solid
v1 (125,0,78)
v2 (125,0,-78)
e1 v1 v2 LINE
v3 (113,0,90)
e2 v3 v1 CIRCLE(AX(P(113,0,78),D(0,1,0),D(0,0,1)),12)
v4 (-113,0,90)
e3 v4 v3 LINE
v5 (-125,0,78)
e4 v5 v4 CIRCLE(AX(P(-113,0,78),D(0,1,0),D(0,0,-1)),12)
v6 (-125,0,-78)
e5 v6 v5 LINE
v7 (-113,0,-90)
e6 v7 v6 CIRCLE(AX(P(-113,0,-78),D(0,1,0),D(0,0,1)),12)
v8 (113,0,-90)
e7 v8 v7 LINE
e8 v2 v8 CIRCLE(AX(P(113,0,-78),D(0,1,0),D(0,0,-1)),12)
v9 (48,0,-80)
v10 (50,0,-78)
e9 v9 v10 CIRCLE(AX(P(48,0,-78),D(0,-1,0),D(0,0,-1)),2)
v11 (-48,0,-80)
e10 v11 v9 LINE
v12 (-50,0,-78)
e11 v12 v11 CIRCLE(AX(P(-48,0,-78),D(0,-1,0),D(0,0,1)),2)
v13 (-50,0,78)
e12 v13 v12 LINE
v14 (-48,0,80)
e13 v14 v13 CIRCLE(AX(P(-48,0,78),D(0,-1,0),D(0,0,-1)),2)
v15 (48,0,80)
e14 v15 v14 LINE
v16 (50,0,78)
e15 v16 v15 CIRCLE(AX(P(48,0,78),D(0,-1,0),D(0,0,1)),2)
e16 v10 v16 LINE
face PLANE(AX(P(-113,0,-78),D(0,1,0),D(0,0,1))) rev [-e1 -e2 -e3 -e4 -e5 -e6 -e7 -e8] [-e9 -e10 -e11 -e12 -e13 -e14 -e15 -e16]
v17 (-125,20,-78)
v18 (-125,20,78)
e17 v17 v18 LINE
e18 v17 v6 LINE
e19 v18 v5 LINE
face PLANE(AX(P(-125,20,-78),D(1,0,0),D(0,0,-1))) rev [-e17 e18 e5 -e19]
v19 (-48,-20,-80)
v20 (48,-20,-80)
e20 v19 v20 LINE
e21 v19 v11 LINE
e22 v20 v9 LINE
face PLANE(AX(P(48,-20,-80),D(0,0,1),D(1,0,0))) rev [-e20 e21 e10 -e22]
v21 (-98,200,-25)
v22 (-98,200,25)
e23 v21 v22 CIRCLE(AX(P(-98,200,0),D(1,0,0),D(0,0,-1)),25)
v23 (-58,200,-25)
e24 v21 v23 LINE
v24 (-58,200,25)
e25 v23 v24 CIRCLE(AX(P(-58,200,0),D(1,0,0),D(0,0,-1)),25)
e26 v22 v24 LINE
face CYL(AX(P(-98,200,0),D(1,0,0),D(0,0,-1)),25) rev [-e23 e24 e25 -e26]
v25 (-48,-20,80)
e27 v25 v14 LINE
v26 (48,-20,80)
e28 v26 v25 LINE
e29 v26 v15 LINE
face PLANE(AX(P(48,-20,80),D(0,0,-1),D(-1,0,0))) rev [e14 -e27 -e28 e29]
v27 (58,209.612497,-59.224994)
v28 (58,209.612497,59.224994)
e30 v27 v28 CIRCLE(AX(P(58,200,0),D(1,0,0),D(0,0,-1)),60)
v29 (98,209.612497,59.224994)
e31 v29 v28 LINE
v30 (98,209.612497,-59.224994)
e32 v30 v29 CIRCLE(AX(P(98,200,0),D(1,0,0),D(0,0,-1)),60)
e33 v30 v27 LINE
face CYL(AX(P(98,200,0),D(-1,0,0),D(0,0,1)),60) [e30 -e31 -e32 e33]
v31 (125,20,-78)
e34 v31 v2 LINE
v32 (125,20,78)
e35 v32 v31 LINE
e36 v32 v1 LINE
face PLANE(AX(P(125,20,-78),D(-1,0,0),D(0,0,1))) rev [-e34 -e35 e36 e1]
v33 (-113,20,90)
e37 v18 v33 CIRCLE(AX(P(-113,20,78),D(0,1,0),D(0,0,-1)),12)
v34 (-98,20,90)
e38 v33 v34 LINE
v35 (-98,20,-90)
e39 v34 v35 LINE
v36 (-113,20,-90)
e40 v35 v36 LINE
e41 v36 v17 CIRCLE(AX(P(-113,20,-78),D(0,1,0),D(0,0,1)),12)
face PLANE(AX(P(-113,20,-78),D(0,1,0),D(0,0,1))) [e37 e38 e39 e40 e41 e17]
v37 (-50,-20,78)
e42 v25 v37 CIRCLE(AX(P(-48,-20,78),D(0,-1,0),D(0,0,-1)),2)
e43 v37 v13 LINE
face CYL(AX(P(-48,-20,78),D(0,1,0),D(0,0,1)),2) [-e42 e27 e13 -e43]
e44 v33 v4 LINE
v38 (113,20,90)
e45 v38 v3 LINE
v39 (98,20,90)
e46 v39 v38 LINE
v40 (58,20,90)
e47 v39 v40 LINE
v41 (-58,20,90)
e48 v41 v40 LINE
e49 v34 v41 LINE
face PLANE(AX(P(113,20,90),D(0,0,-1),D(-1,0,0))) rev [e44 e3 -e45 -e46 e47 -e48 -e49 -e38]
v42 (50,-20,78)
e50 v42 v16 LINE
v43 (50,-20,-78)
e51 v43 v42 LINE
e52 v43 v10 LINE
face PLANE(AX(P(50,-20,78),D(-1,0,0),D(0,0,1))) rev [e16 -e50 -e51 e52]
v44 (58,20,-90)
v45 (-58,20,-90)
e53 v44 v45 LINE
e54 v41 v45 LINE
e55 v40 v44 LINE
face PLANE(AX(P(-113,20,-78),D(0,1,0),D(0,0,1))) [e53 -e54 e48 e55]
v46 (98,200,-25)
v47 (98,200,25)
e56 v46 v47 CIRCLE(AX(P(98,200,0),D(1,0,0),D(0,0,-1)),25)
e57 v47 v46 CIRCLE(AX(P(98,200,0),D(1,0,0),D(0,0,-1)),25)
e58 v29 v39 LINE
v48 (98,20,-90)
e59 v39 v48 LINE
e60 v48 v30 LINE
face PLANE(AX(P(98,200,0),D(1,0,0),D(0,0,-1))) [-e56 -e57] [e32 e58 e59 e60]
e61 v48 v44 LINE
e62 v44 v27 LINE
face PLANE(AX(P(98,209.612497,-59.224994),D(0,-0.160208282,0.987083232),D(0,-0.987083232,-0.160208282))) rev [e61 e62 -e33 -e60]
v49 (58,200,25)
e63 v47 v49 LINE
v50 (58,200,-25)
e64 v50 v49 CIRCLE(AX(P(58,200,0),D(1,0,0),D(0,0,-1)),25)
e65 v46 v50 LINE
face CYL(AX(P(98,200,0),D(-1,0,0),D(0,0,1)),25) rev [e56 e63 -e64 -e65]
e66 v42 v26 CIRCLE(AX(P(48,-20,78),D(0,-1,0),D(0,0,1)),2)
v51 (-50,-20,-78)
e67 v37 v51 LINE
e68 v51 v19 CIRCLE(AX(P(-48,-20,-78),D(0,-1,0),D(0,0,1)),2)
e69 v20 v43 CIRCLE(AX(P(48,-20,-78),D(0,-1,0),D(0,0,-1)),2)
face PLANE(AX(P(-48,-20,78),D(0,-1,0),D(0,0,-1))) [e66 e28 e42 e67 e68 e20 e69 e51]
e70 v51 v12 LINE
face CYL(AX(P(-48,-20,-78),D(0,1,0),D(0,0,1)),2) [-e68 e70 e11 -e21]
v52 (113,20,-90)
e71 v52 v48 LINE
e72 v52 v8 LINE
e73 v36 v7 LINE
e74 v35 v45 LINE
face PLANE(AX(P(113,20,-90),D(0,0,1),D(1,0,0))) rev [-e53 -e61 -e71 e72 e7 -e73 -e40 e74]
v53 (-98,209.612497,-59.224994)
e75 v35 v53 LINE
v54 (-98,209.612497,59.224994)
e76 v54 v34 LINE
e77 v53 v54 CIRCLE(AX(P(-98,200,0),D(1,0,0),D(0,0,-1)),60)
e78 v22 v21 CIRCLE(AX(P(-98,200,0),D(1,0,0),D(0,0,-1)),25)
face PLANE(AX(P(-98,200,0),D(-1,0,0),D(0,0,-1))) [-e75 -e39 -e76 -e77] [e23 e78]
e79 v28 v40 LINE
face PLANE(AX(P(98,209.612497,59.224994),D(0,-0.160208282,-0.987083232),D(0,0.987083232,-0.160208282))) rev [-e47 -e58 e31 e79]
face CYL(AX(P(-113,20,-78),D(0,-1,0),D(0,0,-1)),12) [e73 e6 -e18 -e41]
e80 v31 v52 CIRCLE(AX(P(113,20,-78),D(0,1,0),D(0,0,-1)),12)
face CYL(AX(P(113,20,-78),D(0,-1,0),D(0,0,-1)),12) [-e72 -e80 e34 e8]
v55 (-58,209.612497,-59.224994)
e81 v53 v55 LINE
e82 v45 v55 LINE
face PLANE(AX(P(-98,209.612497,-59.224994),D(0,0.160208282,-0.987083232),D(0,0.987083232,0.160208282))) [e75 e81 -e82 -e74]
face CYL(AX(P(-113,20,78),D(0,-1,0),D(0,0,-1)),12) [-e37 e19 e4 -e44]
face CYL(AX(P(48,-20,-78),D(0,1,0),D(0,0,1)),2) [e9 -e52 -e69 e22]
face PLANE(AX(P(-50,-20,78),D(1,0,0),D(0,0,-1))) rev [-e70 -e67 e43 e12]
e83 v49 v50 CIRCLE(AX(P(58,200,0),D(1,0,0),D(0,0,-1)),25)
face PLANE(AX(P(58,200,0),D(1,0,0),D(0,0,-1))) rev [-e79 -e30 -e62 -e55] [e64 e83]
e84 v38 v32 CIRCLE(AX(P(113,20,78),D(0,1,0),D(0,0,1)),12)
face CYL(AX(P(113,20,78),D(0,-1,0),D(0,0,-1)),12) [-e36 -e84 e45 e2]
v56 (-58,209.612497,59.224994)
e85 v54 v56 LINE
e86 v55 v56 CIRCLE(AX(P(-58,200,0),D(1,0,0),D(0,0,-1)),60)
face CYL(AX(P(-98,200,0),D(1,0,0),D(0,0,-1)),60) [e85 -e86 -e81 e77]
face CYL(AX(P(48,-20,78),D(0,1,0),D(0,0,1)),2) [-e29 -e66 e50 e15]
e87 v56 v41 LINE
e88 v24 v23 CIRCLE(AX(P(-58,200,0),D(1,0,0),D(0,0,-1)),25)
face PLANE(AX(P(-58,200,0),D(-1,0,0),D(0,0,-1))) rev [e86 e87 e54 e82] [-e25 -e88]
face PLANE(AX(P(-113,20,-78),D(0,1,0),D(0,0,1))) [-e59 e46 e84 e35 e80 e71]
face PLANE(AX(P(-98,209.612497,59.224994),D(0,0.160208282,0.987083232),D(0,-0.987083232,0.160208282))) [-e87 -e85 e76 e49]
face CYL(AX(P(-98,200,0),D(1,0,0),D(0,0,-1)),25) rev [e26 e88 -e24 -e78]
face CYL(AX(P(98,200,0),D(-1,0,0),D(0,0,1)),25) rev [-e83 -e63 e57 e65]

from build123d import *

# Parameters (mm, degrees)
BOSS_EXTRUDE_1_DEPTH = 20
BOSS_EXTRUDE_2_DEPTH = 20
BOSS_EXTRUDE_START   = 58
SKETCH_3_R           = 25
BOSS_EXTRUDE_3_DEPTH = 40


with BuildPart() as part:
    # Sketch 1 → Boss-Extrude 1 (new body)
    with BuildSketch(Plane(origin=(0, 0, 0), x_dir=(1, 0, 0), z_dir=(0, 1, 0))):
        with BuildLine():
            Line((113, 90), (-113, 90))
            ThreePointArc((-113, 90), (-121.485281374, 86.485281374), (-125, 78))
            Line((-125, 78), (-125, -78))
            ThreePointArc((-125, -78), (-121.485281374, -86.485281374), (-113, -90))
            Line((-113, -90), (113, -90))
            ThreePointArc((113, -90), (121.485281374, -86.485281374), (125, -78))
            Line((125, -78), (125, 78))
            ThreePointArc((125, 78), (121.485281374, 86.485281374), (113, 90))
        make_face()
    extrude(amount=BOSS_EXTRUDE_1_DEPTH)

    # Sketch 2 → Boss-Extrude 2 (add)
    with BuildSketch(Plane.XZ):
        with BuildLine():
            Line((48, 80), (-48, 80))
            ThreePointArc((-48, 80), (-49.414213562, 79.414213562), (-50, 78))
            Line((-50, 78), (-50, -78))
            ThreePointArc((-50, -78), (-49.414213562, -79.414213562), (-48, -80))
            Line((-48, -80), (48, -80))
            ThreePointArc((48, -80), (49.414213562, -79.414213562), (50, -78))
            Line((50, -78), (50, 78))
            ThreePointArc((50, 78), (49.414213562, 79.414213562), (48, 80))
        make_face()
    extrude(amount=BOSS_EXTRUDE_2_DEPTH)

    # Sketch 3 → Boss-Extrude 3 (add)
    with BuildSketch(Plane(origin=(0, 0, 0), x_dir=(0, 0, -1), z_dir=(1, 0, 0)).offset(BOSS_EXTRUDE_START)):
        with BuildLine():
            Line((-59.224993899, 209.61249695), (-90, 20))
            Line((-90, 20), (90, 20))
            Line((90, 20), (59.224993899, 209.61249695))
            ThreePointArc((59.224993899, 209.61249695), (0, 260), (-59.224993899, 209.61249695))
        make_face()
        with Locations((0, 200)):
            Circle(SKETCH_3_R, mode=Mode.SUBTRACT)
    boss_extrude_3 = extrude(amount=BOSS_EXTRUDE_3_DEPTH)

    # Mirror 1: Boss-Extrude 3 across plane
    add(boss_extrude_3.mirror(Plane(origin=(0, 0, 0), x_dir=(0, 0, 1), z_dir=(1, 0, 0))))


solid = part.part
